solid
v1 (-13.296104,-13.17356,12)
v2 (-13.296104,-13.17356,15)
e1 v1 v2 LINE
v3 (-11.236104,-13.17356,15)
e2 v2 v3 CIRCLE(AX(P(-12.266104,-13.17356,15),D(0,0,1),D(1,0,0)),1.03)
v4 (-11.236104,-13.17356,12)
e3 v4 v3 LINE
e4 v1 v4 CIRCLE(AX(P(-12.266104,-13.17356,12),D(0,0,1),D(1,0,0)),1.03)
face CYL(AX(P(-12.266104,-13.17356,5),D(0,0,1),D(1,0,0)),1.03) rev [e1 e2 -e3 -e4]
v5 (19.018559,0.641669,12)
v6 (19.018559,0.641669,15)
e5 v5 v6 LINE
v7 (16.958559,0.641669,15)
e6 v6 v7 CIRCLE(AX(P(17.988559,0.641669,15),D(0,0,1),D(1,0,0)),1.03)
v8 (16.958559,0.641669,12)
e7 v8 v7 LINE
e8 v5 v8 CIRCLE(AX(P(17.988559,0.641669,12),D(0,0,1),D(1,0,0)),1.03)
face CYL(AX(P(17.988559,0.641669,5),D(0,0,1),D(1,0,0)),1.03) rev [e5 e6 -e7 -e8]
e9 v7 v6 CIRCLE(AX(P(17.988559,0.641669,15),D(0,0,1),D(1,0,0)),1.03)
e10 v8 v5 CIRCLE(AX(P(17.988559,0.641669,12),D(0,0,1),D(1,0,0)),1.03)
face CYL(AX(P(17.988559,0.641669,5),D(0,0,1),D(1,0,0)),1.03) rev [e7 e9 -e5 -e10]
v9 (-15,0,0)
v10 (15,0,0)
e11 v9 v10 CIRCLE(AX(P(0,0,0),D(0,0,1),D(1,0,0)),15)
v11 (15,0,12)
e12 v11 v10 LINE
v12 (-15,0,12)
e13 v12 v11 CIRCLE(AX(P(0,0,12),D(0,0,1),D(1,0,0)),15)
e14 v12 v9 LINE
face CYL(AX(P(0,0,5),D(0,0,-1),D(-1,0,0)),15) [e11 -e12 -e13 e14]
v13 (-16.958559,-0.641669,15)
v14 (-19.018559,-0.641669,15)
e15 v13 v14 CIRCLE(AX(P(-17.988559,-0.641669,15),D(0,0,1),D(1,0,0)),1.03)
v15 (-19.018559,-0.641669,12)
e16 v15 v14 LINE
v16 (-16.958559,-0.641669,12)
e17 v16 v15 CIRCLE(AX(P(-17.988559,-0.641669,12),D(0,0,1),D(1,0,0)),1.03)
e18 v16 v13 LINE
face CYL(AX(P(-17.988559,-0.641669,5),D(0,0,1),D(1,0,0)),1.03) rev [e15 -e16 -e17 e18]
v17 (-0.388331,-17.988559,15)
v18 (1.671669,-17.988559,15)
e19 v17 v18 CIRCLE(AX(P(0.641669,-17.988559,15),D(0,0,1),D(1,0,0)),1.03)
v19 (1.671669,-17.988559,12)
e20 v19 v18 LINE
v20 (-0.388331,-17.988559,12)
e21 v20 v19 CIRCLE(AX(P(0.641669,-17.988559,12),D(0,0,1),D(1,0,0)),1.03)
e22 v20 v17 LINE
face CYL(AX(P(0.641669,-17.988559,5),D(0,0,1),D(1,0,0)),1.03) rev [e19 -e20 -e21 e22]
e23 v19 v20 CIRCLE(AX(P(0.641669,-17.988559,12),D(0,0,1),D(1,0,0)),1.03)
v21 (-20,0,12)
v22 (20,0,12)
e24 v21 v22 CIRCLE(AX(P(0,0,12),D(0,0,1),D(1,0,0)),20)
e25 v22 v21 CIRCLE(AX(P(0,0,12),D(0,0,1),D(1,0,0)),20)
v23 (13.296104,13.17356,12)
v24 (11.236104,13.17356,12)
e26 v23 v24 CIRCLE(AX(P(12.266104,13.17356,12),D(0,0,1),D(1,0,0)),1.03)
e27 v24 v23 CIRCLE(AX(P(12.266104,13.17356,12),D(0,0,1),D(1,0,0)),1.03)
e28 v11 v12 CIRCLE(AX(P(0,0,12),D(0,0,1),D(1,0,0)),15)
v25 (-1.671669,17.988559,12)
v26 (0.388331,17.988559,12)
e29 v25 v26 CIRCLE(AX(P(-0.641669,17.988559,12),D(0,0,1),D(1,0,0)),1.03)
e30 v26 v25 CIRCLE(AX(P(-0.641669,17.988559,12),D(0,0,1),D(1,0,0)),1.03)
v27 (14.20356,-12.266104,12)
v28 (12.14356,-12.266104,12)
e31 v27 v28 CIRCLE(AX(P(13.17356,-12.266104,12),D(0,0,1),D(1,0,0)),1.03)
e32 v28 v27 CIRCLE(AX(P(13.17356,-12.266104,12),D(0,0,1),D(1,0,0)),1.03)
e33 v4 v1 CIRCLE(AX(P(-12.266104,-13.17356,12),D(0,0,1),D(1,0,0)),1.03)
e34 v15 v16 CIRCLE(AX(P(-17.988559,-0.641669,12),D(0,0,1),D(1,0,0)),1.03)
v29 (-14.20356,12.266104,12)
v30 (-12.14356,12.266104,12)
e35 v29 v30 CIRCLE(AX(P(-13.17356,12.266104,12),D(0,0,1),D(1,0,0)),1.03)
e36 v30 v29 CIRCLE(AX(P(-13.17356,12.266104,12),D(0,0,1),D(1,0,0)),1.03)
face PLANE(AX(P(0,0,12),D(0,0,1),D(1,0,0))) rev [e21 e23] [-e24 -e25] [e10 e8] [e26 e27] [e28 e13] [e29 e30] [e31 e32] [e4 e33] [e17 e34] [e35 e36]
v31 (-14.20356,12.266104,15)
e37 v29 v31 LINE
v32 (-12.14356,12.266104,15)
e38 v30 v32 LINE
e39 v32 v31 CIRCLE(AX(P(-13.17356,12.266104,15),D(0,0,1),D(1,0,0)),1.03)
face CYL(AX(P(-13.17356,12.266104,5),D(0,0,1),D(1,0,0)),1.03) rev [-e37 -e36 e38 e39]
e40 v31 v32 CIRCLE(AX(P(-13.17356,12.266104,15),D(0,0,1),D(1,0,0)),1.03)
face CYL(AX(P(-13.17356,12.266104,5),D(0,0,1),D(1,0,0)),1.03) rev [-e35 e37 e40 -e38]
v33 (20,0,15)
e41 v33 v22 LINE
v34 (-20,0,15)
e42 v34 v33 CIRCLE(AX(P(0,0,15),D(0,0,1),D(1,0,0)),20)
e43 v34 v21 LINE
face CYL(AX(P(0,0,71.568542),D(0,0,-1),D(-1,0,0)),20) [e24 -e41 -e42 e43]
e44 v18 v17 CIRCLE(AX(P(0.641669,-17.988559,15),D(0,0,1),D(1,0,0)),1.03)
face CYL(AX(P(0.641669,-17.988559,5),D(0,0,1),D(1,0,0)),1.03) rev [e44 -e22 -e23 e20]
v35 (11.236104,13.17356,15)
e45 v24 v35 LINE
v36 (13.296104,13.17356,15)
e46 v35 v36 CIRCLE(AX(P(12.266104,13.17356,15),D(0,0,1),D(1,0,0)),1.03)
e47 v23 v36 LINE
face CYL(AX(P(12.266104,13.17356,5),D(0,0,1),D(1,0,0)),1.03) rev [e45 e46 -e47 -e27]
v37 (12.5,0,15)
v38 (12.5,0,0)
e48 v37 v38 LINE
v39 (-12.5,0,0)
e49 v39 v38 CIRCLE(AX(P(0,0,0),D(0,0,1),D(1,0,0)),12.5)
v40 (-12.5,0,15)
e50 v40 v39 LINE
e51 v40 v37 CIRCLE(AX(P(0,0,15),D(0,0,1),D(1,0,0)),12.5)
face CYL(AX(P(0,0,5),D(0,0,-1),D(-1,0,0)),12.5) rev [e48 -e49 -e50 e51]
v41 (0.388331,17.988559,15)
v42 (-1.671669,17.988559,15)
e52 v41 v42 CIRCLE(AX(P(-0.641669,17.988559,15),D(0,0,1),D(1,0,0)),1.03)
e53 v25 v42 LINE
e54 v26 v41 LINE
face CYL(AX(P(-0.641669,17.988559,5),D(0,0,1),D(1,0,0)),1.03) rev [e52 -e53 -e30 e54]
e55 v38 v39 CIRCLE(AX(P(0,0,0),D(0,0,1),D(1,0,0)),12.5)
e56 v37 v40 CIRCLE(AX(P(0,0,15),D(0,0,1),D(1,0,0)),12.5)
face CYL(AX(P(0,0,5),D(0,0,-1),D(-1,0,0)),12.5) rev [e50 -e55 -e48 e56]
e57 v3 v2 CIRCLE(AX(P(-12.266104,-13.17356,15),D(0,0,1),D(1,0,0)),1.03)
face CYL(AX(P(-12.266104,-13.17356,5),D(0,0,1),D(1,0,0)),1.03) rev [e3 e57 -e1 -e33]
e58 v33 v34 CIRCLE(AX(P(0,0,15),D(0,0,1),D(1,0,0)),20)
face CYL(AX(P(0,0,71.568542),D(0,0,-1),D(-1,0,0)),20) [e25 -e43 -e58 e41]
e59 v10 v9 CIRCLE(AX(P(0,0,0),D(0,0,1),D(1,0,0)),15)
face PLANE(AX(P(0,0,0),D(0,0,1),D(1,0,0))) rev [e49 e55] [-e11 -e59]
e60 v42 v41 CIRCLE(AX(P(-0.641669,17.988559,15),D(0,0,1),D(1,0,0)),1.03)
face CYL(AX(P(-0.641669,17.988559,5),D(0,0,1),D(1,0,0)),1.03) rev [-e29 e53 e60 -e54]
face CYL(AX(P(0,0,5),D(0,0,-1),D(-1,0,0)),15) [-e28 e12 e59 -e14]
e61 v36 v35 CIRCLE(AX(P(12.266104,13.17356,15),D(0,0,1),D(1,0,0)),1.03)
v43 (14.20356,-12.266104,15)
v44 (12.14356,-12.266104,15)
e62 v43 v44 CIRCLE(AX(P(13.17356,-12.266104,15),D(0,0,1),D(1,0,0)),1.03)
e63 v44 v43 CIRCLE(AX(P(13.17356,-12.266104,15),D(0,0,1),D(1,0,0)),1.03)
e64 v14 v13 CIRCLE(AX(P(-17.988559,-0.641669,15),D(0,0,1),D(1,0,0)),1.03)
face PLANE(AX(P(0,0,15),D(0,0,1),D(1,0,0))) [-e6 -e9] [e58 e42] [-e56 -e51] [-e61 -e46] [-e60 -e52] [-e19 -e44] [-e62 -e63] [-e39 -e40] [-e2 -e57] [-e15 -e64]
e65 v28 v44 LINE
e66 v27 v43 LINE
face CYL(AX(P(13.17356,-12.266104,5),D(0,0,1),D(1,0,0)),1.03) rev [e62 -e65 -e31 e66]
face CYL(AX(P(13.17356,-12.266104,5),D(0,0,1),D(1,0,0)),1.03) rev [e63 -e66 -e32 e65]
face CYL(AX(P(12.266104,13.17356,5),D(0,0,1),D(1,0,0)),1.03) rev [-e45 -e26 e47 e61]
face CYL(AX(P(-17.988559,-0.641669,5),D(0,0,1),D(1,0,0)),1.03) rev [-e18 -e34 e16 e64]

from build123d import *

# Parameters (mm, degrees)
SKETCH1_R           = 15
SKETCH1_R_2         = 12.5
BOSS_EXTRUDE1_DEPTH = 5
SKETCH2_R           = 15
SKETCH2_R_2         = 12.5
BOSS_EXTRUDE2_DEPTH = 10
SKETCH3_R           = 20
SKETCH3_R_2         = 14.885772681
BOSS_EXTRUDE5_DEPTH = 3
SKETCH6_R           = 1.03
CUT_EXTRUDE9_DEPTH  = 10


with BuildPart() as part:
    # Sketch1 → Boss-Extrude1 (new body)
    with BuildSketch(Plane.XY):
        Circle(SKETCH1_R)
        Circle(SKETCH1_R_2, mode=Mode.SUBTRACT)
    extrude(amount=BOSS_EXTRUDE1_DEPTH)

    # Sketch2 → Boss-Extrude2 (add)
    with BuildSketch(Plane.XY.offset(5)):
        Circle(SKETCH2_R)
        Circle(SKETCH2_R_2, mode=Mode.SUBTRACT)
    extrude(amount=BOSS_EXTRUDE2_DEPTH)

    # Sketch3 → Boss-Extrude5 (add)
    with BuildSketch(Plane.XY.offset(12)):
        Circle(SKETCH3_R)
        Circle(SKETCH3_R_2, mode=Mode.SUBTRACT)
    extrude(amount=BOSS_EXTRUDE5_DEPTH)

    # Sketch6 → Cut-Extrude9 (cut)
    with BuildSketch(Plane.XY.offset(15)):
        with Locations((17.988559183, 0.641668533)):
            Circle(SKETCH6_R)
        with Locations((13.173560353, -12.266104012)):
            Circle(SKETCH6_R)
        with Locations((0.641668533, -17.988559183)):
            Circle(SKETCH6_R)
        with Locations((-12.266104012, -13.173560353)):
            Circle(SKETCH6_R)
        with Locations((-17.988559183, -0.641668533)):
            Circle(SKETCH6_R)
        with Locations((-13.173560353, 12.266104012)):
            Circle(SKETCH6_R)
        with Locations((-0.641668533, 17.988559183)):
            Circle(SKETCH6_R)
        with Locations((12.266104012, 13.173560353)):
            Circle(SKETCH6_R)
    extrude(amount=-CUT_EXTRUDE9_DEPTH, mode=Mode.SUBTRACT)


solid = part.part
